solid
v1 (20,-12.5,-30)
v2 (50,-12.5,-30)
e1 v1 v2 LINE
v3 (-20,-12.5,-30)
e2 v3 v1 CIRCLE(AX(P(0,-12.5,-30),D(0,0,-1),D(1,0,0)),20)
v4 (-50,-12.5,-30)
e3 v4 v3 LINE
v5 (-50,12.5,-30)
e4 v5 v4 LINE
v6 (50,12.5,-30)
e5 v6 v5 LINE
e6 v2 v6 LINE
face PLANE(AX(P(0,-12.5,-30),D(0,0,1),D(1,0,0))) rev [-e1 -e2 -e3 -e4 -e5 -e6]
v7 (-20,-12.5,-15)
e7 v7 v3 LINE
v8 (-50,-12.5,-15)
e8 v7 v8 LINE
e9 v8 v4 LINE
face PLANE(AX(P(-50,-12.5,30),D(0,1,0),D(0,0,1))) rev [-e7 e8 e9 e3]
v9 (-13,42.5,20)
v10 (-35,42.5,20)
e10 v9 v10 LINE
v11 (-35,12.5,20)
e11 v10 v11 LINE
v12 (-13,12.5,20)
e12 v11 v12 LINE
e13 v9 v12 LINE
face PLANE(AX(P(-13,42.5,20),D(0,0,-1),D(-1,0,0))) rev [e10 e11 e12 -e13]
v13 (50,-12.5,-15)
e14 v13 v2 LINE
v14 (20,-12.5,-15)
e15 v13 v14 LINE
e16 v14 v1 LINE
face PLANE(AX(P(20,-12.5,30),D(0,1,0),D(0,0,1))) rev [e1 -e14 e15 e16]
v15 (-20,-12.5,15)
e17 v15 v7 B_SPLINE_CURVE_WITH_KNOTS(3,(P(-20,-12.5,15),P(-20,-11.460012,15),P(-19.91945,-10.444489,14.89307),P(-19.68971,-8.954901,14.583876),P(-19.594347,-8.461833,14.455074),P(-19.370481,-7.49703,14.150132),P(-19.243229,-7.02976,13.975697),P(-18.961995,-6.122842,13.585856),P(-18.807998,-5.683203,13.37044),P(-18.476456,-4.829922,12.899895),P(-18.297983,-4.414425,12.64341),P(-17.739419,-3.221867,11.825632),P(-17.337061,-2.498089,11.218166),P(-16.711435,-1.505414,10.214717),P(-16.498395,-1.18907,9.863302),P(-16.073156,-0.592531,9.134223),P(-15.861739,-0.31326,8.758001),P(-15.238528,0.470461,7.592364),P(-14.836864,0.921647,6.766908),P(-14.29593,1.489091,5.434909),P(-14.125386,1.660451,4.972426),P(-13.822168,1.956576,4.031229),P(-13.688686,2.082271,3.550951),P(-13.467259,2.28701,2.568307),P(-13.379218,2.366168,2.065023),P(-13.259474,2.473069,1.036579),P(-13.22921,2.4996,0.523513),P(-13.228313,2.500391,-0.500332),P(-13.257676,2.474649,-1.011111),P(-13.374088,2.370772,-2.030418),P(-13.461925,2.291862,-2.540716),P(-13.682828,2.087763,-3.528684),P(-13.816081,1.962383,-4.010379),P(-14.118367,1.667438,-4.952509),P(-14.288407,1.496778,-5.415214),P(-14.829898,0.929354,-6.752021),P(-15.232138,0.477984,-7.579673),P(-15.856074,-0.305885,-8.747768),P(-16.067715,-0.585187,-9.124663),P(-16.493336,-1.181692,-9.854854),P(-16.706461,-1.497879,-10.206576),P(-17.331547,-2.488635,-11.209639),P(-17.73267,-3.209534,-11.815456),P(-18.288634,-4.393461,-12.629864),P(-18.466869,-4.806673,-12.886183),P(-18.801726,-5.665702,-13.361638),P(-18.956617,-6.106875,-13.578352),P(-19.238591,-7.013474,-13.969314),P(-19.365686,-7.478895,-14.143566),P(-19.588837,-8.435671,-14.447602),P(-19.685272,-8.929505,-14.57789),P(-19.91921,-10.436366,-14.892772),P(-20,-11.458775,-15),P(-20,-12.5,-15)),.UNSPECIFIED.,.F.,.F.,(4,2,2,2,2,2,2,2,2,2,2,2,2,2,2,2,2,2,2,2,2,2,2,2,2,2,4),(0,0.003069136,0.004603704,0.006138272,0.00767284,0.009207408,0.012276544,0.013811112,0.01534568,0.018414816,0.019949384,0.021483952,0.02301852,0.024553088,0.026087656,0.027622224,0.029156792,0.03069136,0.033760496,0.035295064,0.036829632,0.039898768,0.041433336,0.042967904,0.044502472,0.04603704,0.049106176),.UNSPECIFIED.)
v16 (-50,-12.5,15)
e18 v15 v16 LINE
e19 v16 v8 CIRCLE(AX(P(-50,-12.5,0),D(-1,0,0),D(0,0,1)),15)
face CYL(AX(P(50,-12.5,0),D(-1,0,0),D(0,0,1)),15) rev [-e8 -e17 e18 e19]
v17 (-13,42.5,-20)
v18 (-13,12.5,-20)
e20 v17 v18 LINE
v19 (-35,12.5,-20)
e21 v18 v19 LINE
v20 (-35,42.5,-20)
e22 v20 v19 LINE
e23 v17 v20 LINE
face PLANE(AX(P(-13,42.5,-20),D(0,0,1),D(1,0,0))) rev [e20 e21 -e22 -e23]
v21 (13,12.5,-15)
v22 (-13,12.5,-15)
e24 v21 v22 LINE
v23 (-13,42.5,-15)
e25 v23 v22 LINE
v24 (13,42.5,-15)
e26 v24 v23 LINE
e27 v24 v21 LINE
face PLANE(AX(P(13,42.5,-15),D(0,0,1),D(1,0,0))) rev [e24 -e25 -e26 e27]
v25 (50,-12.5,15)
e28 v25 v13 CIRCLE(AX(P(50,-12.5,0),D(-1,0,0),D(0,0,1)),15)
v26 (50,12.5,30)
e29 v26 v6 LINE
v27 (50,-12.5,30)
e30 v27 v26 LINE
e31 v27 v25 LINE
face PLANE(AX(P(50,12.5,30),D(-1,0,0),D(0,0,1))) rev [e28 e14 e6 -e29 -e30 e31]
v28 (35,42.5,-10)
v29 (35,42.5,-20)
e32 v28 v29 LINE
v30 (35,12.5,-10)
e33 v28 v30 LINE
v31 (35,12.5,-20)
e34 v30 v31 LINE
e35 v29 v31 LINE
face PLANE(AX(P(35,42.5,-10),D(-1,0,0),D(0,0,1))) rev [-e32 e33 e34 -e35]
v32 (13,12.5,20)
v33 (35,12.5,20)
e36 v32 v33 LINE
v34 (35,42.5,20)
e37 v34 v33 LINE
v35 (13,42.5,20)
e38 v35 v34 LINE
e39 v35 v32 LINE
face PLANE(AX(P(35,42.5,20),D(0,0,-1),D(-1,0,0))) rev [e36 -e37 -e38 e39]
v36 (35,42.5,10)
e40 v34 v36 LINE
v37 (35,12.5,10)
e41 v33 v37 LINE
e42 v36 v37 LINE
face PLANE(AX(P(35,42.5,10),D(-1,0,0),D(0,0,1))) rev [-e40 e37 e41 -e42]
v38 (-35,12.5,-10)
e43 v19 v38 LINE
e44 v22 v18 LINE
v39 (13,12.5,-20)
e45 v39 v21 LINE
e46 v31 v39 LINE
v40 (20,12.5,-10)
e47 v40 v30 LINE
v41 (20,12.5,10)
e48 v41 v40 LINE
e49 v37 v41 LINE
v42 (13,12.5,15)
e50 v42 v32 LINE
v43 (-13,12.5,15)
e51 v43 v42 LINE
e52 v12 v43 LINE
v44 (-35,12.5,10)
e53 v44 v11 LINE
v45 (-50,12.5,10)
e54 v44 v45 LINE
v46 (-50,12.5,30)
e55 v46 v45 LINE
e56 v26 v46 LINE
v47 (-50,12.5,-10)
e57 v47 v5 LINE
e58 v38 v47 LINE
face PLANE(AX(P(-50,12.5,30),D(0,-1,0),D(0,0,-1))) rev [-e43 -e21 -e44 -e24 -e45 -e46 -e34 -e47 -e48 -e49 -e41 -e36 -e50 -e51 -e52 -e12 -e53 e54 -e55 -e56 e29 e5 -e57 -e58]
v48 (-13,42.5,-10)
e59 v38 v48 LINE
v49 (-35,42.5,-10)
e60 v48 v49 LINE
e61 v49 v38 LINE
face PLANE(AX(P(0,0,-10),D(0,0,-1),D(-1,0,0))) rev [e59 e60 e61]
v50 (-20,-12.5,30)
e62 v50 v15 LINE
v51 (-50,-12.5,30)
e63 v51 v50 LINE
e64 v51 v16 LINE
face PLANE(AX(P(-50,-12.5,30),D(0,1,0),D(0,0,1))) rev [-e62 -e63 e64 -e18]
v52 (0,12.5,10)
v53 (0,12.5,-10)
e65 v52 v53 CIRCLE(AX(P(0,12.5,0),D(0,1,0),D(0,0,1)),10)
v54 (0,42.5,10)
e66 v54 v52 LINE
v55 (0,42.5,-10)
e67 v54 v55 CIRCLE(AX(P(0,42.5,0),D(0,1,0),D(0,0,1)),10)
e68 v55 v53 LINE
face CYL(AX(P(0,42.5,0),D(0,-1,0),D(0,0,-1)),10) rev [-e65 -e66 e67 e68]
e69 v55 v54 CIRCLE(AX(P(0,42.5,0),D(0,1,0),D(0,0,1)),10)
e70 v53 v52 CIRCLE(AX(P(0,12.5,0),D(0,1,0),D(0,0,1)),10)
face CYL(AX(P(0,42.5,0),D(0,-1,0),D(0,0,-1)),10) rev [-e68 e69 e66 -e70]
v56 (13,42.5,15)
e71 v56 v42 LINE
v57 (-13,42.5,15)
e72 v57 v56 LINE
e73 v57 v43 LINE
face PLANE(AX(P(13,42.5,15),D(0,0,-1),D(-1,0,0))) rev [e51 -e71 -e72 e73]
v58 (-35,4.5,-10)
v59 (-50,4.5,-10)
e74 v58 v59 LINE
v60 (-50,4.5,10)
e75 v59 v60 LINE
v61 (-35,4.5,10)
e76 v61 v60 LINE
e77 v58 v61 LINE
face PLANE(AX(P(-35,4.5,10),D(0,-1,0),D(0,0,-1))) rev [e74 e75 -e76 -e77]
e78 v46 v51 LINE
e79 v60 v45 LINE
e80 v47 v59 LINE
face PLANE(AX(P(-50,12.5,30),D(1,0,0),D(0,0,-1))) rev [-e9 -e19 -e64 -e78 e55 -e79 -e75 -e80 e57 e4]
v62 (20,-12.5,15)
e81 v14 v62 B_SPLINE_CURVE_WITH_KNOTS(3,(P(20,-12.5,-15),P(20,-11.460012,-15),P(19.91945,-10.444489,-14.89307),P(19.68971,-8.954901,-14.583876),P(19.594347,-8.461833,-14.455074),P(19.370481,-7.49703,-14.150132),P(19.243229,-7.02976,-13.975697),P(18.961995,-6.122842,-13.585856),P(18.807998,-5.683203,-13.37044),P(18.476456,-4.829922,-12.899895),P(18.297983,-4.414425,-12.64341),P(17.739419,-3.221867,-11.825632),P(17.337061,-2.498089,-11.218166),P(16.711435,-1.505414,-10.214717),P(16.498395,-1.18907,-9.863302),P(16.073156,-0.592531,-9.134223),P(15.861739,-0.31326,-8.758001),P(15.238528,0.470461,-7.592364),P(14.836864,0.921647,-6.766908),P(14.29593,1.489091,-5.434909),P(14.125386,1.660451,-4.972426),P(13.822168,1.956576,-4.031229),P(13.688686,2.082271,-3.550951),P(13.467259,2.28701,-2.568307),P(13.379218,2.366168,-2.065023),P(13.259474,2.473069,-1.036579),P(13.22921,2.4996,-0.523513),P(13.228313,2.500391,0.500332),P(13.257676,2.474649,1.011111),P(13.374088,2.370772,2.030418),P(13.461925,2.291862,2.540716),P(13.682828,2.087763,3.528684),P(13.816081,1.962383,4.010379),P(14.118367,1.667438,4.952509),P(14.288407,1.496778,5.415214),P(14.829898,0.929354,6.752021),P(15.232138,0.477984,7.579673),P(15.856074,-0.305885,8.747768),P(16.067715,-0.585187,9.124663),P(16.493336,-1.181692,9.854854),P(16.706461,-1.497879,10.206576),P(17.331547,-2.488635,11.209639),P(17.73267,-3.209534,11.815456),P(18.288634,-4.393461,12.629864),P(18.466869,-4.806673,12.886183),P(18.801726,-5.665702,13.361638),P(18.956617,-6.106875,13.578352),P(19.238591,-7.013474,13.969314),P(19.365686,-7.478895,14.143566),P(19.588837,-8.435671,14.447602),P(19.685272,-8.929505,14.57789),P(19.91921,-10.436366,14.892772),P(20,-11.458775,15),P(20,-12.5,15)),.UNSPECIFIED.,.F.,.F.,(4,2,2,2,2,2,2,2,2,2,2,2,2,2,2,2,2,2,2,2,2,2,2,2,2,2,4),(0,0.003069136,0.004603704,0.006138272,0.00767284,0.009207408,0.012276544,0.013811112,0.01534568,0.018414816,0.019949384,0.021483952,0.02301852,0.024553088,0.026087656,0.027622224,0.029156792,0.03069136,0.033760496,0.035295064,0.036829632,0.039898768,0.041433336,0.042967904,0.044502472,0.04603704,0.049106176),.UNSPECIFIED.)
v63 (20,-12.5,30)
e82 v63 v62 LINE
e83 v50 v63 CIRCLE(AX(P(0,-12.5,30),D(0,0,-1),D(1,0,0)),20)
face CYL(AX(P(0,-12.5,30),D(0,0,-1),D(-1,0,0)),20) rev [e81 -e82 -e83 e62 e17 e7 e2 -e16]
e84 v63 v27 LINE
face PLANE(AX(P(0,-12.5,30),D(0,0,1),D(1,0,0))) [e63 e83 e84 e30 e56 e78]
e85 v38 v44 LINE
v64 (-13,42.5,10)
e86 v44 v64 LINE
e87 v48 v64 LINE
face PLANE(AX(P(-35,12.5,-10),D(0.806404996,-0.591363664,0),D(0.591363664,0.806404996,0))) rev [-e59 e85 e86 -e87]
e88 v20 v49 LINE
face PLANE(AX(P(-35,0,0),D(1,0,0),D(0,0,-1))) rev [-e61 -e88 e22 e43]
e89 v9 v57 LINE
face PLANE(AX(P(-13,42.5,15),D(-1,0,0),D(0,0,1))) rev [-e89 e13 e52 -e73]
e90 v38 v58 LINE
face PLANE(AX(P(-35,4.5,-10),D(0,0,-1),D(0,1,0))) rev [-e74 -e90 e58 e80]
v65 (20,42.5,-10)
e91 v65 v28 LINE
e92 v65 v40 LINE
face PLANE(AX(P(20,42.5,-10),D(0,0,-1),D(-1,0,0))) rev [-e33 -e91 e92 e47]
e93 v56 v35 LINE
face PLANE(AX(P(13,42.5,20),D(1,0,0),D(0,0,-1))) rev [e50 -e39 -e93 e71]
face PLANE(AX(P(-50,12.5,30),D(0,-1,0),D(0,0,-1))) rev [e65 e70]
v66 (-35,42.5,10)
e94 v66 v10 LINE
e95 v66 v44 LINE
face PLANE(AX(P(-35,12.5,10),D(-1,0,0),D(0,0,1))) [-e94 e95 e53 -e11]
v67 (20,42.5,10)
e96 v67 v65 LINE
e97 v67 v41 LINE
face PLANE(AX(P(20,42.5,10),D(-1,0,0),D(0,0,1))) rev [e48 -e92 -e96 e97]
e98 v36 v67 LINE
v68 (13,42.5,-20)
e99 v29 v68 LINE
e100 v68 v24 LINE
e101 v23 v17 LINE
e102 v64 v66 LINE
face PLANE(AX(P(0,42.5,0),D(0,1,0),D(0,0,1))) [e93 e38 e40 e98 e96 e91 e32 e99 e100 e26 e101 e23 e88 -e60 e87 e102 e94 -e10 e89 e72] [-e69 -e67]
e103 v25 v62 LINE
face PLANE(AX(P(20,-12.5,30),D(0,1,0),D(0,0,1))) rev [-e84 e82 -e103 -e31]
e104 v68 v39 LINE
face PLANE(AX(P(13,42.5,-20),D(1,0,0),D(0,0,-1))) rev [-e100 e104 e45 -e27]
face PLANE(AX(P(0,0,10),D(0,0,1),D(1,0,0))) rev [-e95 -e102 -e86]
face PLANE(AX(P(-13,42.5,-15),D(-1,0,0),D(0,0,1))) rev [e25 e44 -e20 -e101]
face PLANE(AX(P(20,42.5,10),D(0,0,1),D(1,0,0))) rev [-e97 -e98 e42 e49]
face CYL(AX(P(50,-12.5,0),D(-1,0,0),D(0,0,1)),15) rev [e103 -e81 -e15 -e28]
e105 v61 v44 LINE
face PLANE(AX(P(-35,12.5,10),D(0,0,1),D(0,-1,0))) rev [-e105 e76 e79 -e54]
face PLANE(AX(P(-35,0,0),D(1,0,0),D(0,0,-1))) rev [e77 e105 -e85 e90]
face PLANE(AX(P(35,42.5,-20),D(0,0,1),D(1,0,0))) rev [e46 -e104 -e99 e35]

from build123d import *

# Parameters (mm, degrees)
SADDLE_BASE_BLOCK_DEPTH     = 30
THROUGH_HOLE_15_DEPTH       = 106.148704224
SLOT_CUT_DEPTH              = 15
CROSS_BOSS_PROFILE_SKETCH_R = 10
CROSS_BOSS_DEPTH            = 30
UPPER_PAD_SKETCH_W          = 20
UPPER_PAD_SKETCH_H          = 30
UPPER_PAD_DEPTH             = 15
NOTCH_CUT_DEPTH             = 30
NOTCH_FILL_BOSS_DEPTH       = 10


with BuildPart() as part:
    # Base Arch Profile Sketch → Saddle Base Block (new, symmetric)
    with BuildSketch(Plane.XY):
        with BuildLine():
            Line((20, -12.5), (50, -12.5))
            Line((50, -12.5), (50, 12.5))
            Line((50, 12.5), (-50, 12.5))
            Line((-50, 12.5), (-50, -12.5))
            Line((-50, -12.5), (-20, -12.5))
            ThreePointArc((-20, -12.5), (0, 7.5), (20, -12.5))
        make_face()
    extrude(amount=SADDLE_BASE_BLOCK_DEPTH, both=True)

    # Through Hole Sketch → Through Hole Ø15 (cut, through all)
    with BuildSketch(Plane.ZY.offset(50)):
        with BuildLine():
            Line((-15, -12.5), (15, -12.5))
            ThreePointArc((15, -12.5), (0, 2.5), (-15, -12.5))
        make_face()
    extrude(amount=-THROUGH_HOLE_15_DEPTH, mode=Mode.SUBTRACT)

    # Slot Profile Sketch → Slot Cut (cut)
    with BuildSketch(Plane.ZY.offset(50)):
        Polygon((0, 12.5), (10, 12.5), (10, 4.5), (-10, 4.5), (-10, 12.5), align=None)
    extrude(amount=-SLOT_CUT_DEPTH, mode=Mode.SUBTRACT)

    # Cross Boss Profile Sketch → Cross Boss (add)
    with BuildSketch(Plane(origin=(0, 12.5, 0), x_dir=(1, 0, 0), z_dir=(0, 1, 0))):
        Polygon((20, -10), (20, 10), (35, 10), (35, 20), (13, 20), (13, 15), (-13, 15), (-13, 20), (-35, 20), (-35, 10), (-20, 10), (-20, -10), (-35, -10), (-35, -20), (-13, -20), (-13, -15), (13, -15), (13, -20), (35, -20), (35, -10), align=None)
        with Locations(Location((0, 0, 0), (0, 0, 270))):
            Circle(CROSS_BOSS_PROFILE_SKETCH_R, mode=Mode.SUBTRACT)
    extrude(amount=CROSS_BOSS_DEPTH)

    # Upper Pad Sketch → Upper Pad (add)
    with BuildSketch(Plane.ZY.offset(20)):
        with Locations((0, 27.5)):
            Rectangle(UPPER_PAD_SKETCH_W, UPPER_PAD_SKETCH_H)
    extrude(amount=UPPER_PAD_DEPTH)

    # Notch Cut Sketch → Notch Cut (cut)
    with BuildSketch(Plane.XY.offset(20)):
        Polygon((-35, 12.5), (-13, 42.5), (-35, 42.5), align=None)
    extrude(amount=-NOTCH_CUT_DEPTH, mode=Mode.SUBTRACT)

    # Notch Fill Sketch → Notch Fill Boss (add)
    with BuildSketch(Plane.XY.offset(20)):
        Polygon((-35, 12.5), (-35, 42.5), (-13, 42.5), align=None)
    extrude(amount=-NOTCH_FILL_BOSS_DEPTH)


solid = part.part
